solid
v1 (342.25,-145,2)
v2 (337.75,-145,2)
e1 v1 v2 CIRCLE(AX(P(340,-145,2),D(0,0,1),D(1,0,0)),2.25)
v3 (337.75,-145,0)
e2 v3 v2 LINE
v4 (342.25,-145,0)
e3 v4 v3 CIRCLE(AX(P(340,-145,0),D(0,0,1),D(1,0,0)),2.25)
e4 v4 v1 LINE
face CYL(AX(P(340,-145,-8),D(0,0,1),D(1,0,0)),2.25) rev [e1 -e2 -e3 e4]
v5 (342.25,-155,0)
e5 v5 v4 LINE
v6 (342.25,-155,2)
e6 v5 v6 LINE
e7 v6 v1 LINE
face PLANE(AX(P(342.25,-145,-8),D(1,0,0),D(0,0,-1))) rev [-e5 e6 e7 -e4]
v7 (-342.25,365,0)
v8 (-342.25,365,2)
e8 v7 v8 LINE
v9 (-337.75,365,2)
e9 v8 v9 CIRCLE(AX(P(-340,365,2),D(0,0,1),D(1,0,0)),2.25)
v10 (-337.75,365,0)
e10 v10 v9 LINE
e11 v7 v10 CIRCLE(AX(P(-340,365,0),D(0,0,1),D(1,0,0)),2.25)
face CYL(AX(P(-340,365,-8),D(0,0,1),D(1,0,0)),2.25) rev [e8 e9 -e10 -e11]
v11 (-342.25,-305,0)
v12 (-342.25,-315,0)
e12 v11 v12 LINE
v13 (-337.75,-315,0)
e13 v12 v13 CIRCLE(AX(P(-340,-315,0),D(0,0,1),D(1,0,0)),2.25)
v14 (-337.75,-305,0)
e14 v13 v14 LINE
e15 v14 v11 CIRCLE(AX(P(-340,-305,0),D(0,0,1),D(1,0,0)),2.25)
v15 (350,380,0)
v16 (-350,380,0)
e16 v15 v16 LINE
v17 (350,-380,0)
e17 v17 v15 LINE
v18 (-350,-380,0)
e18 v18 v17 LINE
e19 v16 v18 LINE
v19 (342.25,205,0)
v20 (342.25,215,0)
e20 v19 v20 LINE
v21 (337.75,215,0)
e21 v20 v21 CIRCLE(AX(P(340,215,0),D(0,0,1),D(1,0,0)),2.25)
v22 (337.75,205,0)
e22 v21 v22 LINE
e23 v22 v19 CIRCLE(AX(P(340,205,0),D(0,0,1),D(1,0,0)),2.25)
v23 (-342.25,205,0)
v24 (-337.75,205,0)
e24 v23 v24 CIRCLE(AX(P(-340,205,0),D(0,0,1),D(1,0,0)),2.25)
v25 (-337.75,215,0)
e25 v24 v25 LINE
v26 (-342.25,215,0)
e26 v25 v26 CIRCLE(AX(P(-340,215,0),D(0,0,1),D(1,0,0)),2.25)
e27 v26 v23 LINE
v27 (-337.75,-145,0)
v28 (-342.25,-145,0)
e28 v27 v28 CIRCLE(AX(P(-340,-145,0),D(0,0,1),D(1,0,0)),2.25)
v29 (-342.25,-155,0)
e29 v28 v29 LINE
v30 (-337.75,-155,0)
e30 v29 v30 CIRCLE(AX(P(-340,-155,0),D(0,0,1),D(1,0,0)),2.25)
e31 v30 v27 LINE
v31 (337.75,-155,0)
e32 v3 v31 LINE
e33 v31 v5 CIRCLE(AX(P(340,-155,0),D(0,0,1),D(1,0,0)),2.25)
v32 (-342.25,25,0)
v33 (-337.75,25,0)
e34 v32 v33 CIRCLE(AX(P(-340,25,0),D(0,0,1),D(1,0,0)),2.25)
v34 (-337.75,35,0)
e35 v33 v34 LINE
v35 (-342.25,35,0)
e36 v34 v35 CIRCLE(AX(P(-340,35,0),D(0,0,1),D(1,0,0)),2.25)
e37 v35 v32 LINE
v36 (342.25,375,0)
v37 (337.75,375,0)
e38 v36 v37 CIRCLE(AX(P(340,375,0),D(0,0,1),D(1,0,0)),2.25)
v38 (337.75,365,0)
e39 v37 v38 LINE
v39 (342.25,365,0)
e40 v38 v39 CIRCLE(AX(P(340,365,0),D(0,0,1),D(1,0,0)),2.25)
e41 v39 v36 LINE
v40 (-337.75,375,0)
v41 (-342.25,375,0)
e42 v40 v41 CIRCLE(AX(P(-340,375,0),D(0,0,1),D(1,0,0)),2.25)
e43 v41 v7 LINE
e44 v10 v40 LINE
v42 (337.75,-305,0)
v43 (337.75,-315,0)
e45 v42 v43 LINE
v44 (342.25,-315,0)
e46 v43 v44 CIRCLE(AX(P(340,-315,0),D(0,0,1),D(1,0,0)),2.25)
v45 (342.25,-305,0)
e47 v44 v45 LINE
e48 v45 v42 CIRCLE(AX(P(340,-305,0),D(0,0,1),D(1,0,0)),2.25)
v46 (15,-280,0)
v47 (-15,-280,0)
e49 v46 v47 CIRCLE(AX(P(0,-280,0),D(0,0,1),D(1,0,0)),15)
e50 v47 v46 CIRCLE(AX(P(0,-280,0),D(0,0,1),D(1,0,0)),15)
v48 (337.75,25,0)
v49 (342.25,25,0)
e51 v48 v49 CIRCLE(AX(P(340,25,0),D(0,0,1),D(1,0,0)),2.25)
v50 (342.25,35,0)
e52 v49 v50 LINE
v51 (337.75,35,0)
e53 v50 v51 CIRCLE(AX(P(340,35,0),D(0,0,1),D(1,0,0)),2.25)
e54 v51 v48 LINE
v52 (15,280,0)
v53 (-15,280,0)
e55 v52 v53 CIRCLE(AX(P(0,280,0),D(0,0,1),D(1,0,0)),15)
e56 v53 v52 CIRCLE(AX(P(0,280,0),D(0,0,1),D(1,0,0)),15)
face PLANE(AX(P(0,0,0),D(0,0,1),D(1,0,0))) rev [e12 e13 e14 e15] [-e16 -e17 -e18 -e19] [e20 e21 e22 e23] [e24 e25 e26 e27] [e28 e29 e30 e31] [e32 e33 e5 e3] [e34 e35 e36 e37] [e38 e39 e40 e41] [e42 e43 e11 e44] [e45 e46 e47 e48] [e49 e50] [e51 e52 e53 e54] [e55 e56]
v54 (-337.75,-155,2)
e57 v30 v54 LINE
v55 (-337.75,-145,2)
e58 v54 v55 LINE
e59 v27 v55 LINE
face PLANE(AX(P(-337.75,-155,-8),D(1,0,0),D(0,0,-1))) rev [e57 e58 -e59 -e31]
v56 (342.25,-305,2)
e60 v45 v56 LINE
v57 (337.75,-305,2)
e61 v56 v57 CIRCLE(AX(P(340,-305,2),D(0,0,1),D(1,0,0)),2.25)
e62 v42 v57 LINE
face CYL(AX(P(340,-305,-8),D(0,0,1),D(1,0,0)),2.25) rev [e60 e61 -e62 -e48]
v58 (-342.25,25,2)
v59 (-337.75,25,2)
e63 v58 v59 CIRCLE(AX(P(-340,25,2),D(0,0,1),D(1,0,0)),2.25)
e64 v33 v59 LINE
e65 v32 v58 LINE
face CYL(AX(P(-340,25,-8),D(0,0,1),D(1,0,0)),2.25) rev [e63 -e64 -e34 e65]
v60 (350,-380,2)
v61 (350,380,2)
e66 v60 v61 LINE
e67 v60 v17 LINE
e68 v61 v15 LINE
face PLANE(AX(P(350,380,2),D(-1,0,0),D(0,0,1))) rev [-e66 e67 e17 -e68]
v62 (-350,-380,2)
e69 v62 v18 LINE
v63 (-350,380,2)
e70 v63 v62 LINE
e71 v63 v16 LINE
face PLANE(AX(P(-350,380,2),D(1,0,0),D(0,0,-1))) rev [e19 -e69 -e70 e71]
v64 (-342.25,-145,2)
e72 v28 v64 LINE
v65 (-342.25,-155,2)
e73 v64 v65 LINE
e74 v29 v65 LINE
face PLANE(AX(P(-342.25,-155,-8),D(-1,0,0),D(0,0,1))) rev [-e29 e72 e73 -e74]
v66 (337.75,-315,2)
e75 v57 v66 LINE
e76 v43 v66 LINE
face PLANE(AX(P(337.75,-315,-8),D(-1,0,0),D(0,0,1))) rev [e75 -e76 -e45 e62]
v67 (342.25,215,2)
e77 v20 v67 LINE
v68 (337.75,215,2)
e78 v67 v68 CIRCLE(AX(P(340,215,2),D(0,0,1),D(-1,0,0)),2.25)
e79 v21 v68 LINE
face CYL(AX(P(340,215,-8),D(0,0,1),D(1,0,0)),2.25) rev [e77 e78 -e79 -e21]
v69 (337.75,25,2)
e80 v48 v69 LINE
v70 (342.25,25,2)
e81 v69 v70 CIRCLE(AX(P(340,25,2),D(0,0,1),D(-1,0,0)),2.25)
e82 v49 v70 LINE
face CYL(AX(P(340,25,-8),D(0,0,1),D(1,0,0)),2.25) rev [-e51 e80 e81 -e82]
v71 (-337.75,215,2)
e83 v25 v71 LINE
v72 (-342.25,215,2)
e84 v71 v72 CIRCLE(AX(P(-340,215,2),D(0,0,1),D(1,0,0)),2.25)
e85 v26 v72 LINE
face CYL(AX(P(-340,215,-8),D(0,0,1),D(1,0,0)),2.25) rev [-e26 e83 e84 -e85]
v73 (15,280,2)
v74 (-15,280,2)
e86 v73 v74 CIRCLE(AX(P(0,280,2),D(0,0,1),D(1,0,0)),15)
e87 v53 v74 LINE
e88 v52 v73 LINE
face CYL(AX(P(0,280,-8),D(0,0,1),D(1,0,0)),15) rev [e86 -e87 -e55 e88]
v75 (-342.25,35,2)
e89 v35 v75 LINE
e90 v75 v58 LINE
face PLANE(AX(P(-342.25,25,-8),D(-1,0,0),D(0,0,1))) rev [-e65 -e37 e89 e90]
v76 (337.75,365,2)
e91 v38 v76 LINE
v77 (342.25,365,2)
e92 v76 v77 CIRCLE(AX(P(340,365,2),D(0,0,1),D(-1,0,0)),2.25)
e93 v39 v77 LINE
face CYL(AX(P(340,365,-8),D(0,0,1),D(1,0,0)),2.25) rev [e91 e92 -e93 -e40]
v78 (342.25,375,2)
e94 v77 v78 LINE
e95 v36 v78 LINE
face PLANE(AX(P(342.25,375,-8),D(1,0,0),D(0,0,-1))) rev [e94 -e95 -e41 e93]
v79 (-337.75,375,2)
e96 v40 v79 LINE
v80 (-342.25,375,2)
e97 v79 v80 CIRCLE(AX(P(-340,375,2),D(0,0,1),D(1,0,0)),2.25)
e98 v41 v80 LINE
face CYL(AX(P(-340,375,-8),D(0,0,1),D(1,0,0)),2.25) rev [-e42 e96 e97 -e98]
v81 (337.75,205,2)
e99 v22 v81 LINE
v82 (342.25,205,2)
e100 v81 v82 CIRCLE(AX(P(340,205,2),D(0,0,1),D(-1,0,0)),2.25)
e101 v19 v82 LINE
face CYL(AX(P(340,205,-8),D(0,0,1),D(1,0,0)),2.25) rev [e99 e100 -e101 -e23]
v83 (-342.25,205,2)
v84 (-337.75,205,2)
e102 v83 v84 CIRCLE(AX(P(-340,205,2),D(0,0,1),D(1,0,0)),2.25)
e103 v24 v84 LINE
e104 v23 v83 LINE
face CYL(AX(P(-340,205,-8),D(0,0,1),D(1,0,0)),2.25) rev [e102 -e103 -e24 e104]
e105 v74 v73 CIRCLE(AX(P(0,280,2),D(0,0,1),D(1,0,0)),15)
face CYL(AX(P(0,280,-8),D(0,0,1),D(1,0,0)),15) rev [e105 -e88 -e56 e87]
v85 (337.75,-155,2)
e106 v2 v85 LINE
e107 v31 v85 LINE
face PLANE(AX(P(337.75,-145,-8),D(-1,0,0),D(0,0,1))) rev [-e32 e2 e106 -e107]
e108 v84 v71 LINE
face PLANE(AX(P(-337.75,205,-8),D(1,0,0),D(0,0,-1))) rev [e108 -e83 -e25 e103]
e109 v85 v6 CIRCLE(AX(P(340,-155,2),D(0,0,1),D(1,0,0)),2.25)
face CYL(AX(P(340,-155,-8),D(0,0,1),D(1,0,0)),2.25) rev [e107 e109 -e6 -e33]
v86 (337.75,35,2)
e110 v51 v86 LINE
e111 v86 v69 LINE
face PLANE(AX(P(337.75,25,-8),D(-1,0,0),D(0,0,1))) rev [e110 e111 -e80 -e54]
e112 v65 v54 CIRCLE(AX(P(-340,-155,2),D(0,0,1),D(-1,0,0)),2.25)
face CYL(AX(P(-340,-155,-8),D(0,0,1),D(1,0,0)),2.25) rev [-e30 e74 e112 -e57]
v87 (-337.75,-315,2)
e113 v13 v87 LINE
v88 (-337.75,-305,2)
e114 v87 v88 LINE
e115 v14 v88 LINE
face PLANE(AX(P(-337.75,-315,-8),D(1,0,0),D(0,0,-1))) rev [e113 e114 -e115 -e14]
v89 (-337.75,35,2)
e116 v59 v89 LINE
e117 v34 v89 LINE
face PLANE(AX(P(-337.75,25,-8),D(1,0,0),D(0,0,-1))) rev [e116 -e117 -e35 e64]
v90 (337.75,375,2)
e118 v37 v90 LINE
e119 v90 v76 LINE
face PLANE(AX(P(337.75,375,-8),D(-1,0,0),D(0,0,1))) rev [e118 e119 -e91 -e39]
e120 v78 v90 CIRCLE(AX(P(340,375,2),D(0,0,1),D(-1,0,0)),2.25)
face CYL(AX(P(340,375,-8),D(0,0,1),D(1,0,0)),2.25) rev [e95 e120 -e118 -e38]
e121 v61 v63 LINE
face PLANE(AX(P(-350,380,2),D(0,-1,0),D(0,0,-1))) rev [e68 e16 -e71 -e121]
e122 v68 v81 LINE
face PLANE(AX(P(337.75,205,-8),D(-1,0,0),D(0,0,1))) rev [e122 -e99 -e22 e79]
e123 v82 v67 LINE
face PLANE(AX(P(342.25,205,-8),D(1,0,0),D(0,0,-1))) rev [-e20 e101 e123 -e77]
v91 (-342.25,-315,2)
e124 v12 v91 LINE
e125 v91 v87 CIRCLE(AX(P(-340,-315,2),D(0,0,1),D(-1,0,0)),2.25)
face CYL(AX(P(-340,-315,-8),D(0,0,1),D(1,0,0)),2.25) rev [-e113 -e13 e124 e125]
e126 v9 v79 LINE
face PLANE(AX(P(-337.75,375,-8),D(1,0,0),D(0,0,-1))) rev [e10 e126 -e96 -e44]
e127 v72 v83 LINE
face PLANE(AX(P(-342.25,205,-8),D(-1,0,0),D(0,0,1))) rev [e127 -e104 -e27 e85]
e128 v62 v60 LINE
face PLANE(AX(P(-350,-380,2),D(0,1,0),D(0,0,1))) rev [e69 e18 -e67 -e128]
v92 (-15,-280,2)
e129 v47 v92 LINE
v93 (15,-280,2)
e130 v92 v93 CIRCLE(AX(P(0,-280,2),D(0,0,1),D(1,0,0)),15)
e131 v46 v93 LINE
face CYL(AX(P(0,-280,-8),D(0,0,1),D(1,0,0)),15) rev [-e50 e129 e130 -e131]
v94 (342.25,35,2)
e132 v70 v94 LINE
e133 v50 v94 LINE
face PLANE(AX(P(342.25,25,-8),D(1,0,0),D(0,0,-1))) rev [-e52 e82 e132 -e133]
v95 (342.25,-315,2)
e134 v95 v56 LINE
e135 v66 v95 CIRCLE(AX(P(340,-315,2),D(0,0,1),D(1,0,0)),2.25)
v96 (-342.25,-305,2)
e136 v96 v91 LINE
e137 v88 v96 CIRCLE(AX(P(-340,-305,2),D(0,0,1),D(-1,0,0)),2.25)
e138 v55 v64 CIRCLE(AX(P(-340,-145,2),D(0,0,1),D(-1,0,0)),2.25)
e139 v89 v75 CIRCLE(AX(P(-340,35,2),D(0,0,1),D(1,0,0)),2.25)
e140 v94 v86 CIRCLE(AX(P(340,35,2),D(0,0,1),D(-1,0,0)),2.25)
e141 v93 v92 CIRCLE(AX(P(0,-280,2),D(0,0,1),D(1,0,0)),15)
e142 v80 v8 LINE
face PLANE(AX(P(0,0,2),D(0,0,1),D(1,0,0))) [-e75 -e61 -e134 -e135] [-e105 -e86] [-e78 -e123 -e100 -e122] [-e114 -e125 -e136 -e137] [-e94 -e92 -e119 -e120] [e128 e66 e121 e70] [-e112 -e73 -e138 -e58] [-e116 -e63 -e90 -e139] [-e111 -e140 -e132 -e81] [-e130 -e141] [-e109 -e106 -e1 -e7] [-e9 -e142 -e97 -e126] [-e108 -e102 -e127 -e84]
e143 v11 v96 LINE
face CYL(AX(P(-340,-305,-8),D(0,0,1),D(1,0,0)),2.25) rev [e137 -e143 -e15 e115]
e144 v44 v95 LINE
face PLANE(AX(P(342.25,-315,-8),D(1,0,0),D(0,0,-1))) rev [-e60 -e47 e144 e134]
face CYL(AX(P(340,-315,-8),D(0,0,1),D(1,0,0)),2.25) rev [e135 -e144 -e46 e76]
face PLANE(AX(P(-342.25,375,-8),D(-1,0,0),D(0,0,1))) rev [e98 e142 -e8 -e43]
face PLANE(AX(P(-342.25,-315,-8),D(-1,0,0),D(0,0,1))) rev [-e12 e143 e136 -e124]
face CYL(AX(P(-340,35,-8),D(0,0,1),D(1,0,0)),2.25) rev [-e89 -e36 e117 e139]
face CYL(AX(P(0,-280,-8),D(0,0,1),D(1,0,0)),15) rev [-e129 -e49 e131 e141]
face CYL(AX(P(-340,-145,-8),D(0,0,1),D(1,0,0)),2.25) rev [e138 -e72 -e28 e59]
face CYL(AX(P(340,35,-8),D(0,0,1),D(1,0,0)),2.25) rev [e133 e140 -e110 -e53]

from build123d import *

# Parameters (mm, degrees)
SKETCH_1_W          = 700
SKETCH_1_H          = 760
EXTRUDE_1_DEPTH     = 2
CUT_EXTRUDE_1_DEPTH = 10
SKETCH_3_R          = 15
CUT_EXTRUDE_2_DEPTH = 10


with BuildPart() as part:
    # 草图1 → 凸台-拉伸1 (new body)
    with BuildSketch(Plane.XY):
        Rectangle(SKETCH_1_W, SKETCH_1_H)
    extrude(amount=EXTRUDE_1_DEPTH)

    # 草图2 → 切除-拉伸1 (cut)
    with BuildSketch(Plane.XY.offset(2)):
        with BuildLine():
            Line((-337.75, 375), (-337.75, 365))
            ThreePointArc((-337.75, 365), (-340, 362.75), (-342.25, 365))
            Line((-342.25, 365), (-342.25, 375))
            ThreePointArc((-342.25, 375), (-340, 377.25), (-337.75, 375))
        make_face()
        with BuildLine():
            Line((-342.25, 205), (-342.25, 215))
            ThreePointArc((-342.25, 215), (-340, 217.25), (-337.75, 215))
            Line((-337.75, 215), (-337.75, 205))
            ThreePointArc((-337.75, 205), (-340, 202.75), (-342.25, 205))
        make_face()
        with BuildLine():
            Line((-342.25, 25), (-342.25, 35))
            ThreePointArc((-342.25, 35), (-340, 37.25), (-337.75, 35))
            Line((-337.75, 35), (-337.75, 25))
            ThreePointArc((-337.75, 25), (-340, 22.75), (-342.25, 25))
        make_face()
        with BuildLine():
            Line((337.75, 375), (337.75, 365))
            ThreePointArc((337.75, 365), (340, 362.75), (342.25, 365))
            Line((342.25, 365), (342.25, 375))
            ThreePointArc((342.25, 375), (340, 377.25), (337.75, 375))
        make_face()
        with BuildLine():
            Line((342.25, 205), (342.25, 215))
            ThreePointArc((342.25, 215), (340, 217.25), (337.75, 215))
            Line((337.75, 215), (337.75, 205))
            ThreePointArc((337.75, 205), (340, 202.75), (342.25, 205))
        make_face()
        with BuildLine():
            Line((342.25, 25), (342.25, 35))
            ThreePointArc((342.25, 35), (340, 37.25), (337.75, 35))
            Line((337.75, 35), (337.75, 25))
            ThreePointArc((337.75, 25), (340, 22.75), (342.25, 25))
        make_face()
        with BuildLine():
            Line((-337.75, -315), (-337.75, -305))
            ThreePointArc((-337.75, -305), (-340, -302.75), (-342.25, -305))
            Line((-342.25, -305), (-342.25, -315))
            ThreePointArc((-342.25, -315), (-340, -317.25), (-337.75, -315))
        make_face()
        with BuildLine():
            Line((-337.75, -155), (-337.75, -145))
            ThreePointArc((-337.75, -145), (-340, -142.75), (-342.25, -145))
            Line((-342.25, -145), (-342.25, -155))
            ThreePointArc((-342.25, -155), (-340, -157.25), (-337.75, -155))
        make_face()
        with BuildLine():
            Line((337.75, -315), (337.75, -305))
            ThreePointArc((337.75, -305), (340, -302.75), (342.25, -305))
            Line((342.25, -305), (342.25, -315))
            ThreePointArc((342.25, -315), (340, -317.25), (337.75, -315))
        make_face()
        with BuildLine():
            Line((342.25, -145), (342.25, -155))
            ThreePointArc((342.25, -155), (340, -157.25), (337.75, -155))
            Line((337.75, -155), (337.75, -145))
            ThreePointArc((337.75, -145), (340, -142.75), (342.25, -145))
        make_face()
    extrude(amount=-CUT_EXTRUDE_1_DEPTH, mode=Mode.SUBTRACT)

    # 草图3 → 切除-拉伸2 (cut)
    with BuildSketch(Plane.XY.offset(2)):
        with Locations((0, -280)):
            Circle(SKETCH_3_R)
        with Locations((0, 280)):
            Circle(SKETCH_3_R)
    extrude(amount=-CUT_EXTRUDE_2_DEPTH, mode=Mode.SUBTRACT)


solid = part.part
